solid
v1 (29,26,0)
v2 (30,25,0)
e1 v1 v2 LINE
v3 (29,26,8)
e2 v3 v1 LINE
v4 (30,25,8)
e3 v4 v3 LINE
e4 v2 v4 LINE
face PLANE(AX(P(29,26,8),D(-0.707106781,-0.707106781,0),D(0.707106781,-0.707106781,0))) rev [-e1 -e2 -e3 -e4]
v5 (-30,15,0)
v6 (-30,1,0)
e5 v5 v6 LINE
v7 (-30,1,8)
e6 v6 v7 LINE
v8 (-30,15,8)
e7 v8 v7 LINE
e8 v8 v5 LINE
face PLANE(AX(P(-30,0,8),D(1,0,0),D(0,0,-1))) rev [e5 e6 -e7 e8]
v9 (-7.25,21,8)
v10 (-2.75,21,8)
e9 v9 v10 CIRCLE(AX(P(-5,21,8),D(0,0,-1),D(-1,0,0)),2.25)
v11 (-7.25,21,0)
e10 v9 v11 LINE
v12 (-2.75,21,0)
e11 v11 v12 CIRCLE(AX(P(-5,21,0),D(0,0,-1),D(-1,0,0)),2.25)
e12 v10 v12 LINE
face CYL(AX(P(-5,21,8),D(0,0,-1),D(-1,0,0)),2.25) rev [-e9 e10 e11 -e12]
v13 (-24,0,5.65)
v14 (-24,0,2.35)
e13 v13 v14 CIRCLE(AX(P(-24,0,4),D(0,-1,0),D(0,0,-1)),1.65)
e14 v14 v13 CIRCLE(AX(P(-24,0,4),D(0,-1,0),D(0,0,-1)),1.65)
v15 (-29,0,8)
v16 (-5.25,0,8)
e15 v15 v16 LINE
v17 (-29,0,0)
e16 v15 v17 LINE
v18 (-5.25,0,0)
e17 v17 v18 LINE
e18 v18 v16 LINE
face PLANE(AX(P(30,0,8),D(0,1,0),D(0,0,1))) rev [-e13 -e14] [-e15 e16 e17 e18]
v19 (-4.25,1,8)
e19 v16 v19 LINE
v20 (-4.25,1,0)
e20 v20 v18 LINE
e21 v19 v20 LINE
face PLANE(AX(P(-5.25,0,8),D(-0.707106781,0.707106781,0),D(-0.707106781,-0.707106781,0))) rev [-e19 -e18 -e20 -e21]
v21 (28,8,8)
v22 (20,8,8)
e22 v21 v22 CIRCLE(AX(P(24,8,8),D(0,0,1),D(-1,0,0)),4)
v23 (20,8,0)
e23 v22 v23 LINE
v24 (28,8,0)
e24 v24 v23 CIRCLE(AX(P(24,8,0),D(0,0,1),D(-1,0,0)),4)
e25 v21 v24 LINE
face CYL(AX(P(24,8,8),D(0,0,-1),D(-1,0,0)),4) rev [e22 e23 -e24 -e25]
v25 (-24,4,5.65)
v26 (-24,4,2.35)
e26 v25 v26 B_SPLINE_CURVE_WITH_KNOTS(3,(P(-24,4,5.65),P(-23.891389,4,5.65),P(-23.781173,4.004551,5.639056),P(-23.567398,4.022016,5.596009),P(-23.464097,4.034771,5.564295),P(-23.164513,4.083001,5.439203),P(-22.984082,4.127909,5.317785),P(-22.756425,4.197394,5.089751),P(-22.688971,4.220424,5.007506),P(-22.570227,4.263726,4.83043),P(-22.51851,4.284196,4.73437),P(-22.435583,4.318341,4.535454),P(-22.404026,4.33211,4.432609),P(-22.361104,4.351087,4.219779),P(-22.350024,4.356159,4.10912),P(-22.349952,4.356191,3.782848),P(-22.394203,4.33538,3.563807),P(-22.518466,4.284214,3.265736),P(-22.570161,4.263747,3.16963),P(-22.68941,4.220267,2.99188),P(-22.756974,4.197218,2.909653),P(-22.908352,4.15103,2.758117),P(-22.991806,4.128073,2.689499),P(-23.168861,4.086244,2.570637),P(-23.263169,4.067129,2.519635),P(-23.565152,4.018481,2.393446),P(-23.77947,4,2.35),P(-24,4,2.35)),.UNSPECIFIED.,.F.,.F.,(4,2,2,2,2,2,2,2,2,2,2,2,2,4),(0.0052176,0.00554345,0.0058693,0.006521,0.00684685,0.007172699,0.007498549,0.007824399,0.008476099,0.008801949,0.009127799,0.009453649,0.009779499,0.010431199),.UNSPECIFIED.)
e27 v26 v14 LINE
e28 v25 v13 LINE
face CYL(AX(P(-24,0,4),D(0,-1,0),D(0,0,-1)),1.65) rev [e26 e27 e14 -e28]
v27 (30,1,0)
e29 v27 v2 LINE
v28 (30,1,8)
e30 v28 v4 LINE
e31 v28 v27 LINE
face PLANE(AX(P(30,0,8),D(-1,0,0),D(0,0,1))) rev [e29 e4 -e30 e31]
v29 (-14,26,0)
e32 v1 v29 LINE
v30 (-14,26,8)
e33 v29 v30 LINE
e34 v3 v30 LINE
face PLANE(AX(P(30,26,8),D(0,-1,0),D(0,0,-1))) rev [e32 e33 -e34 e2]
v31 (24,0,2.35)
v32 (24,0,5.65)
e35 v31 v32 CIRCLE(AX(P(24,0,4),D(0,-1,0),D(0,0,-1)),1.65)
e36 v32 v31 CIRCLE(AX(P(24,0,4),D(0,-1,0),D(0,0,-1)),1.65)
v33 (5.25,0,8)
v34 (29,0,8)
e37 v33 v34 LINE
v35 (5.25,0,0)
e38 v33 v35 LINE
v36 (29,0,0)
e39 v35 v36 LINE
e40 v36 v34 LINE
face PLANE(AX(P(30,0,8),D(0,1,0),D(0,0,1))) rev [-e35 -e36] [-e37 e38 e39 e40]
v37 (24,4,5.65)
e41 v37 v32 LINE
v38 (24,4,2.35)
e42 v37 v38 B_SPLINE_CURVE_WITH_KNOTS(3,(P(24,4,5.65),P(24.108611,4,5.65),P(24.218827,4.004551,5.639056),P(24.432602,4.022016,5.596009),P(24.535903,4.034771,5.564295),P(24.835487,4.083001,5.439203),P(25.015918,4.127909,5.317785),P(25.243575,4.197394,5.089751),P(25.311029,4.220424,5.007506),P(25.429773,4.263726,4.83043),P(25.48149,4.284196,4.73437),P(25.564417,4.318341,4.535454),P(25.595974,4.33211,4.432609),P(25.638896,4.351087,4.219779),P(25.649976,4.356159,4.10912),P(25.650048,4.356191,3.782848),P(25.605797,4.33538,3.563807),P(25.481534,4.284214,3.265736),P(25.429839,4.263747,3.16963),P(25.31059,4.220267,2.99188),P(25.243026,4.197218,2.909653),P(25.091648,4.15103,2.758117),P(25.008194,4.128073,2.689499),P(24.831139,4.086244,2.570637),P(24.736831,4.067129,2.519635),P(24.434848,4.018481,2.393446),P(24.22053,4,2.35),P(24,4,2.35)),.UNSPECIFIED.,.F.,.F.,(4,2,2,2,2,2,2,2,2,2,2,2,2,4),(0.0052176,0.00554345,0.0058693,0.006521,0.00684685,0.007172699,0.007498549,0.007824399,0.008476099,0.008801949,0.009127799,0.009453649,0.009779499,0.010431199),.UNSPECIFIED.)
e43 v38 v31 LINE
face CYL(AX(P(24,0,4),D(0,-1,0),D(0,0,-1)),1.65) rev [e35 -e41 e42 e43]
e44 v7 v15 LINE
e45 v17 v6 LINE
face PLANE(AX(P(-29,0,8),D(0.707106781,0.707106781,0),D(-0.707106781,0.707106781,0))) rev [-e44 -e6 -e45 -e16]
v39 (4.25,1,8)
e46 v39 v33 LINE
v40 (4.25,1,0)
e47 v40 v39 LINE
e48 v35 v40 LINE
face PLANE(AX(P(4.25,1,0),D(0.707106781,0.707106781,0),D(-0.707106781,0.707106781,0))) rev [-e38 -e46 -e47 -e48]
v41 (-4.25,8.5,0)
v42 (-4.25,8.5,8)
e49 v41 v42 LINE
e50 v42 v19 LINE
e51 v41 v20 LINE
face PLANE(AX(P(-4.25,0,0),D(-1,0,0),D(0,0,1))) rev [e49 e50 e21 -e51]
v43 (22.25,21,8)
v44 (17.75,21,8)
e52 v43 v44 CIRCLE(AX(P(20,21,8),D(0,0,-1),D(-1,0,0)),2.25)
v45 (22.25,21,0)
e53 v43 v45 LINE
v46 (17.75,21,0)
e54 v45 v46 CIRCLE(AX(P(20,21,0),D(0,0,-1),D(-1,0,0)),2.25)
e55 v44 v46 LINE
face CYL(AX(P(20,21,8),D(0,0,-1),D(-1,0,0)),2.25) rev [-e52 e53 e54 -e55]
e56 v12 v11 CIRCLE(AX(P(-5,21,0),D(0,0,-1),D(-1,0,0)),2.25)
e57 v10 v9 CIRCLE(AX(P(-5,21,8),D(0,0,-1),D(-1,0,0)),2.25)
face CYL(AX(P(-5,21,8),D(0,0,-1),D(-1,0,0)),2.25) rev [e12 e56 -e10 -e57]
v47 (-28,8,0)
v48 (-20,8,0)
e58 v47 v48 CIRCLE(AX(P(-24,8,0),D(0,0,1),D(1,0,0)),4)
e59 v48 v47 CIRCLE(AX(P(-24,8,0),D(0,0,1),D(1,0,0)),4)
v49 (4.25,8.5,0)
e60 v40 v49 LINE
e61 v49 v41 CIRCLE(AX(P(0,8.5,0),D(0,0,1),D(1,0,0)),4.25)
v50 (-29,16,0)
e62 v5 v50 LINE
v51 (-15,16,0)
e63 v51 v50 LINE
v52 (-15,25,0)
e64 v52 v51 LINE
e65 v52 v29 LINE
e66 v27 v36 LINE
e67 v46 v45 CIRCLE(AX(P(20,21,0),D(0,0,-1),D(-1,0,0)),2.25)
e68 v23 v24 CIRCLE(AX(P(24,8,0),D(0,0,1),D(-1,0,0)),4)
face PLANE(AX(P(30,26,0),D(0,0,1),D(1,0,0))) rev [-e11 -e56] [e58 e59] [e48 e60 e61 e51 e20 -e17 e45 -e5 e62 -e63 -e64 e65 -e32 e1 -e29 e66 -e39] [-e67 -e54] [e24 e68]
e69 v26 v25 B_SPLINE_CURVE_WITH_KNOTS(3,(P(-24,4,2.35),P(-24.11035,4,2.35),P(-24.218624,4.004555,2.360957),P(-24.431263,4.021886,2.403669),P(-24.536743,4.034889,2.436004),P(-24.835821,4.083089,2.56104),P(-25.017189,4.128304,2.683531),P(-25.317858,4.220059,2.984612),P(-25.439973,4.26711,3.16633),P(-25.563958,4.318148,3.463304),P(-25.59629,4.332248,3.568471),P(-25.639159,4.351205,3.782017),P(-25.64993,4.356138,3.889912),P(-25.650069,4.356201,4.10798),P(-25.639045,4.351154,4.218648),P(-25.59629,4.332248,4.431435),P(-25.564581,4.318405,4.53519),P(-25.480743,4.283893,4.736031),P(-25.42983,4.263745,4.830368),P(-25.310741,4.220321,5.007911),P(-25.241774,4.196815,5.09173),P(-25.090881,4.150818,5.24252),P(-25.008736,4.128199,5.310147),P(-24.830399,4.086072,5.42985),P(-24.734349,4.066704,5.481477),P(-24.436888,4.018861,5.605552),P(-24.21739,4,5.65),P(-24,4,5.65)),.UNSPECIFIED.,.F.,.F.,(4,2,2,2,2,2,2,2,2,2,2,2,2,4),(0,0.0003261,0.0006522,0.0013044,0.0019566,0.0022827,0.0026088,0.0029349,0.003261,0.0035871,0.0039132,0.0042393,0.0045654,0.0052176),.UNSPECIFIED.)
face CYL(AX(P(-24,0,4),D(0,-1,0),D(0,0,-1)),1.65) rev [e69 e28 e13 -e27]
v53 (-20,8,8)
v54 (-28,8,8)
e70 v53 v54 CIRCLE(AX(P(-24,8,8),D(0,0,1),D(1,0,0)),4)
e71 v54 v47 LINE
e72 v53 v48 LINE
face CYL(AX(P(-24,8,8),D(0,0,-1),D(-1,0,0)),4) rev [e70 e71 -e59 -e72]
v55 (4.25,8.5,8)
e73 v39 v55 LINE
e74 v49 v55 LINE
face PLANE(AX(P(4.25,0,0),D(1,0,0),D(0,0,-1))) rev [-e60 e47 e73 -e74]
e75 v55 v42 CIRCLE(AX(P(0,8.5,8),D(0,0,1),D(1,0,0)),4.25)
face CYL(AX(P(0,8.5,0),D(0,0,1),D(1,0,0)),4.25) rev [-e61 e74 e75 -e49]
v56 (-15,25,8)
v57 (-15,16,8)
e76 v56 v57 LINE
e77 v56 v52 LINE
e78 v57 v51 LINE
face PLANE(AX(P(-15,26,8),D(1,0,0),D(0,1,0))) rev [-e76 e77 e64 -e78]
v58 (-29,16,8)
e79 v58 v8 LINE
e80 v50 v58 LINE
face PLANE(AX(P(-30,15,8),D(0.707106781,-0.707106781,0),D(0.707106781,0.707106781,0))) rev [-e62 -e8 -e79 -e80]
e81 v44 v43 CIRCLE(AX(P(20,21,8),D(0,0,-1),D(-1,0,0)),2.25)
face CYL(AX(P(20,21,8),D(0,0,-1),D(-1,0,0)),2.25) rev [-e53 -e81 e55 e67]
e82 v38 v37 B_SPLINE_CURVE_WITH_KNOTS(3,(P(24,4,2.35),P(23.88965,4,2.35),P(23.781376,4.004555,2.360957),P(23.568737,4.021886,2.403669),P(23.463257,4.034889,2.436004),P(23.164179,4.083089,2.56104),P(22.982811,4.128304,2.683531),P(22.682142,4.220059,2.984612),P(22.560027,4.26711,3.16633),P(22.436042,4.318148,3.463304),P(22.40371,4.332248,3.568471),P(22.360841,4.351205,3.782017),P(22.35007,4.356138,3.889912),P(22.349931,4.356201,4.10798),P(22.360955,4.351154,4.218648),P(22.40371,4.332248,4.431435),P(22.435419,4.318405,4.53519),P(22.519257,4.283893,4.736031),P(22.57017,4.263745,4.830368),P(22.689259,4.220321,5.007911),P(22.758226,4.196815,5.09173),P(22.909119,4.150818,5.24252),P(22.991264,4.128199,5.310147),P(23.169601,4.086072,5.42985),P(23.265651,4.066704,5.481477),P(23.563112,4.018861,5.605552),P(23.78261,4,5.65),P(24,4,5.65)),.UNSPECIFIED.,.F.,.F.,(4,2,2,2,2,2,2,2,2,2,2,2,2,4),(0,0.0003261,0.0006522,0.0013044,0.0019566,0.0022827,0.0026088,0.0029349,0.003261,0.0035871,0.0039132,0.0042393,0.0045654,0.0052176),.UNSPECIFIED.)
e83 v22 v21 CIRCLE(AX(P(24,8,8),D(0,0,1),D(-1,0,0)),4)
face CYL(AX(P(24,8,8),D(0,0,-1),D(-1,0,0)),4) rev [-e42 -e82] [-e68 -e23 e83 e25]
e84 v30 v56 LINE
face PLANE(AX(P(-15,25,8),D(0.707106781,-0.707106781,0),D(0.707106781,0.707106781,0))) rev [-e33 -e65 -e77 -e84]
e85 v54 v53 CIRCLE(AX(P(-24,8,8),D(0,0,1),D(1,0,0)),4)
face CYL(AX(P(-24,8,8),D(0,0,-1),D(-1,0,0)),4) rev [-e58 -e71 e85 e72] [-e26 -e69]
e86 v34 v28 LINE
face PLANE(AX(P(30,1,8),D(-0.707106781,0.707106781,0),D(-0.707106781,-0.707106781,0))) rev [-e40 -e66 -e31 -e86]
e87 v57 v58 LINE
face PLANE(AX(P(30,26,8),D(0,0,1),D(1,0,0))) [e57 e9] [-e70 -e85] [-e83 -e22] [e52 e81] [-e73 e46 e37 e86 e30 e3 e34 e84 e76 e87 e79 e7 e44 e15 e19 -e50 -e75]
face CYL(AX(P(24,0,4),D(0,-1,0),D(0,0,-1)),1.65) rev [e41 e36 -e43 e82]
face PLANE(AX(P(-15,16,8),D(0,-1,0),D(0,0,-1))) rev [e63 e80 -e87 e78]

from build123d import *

# Parameters (mm, degrees)
SKETCH1_W              = 60
SKETCH1_H              = 26
SKETCH1_R              = 4
BOSS_EXTRUDE1_DEPTH    = 8
CUT_EXTRUDE1_DEPTH     = 41.496913463
M4_TAPPED_HOLE1_REACH  = 42.497
M4_TAPPED_HOLE1_BORE_R = 1.65
SKETCH8_W              = 15
SKETCH8_H              = 10
CUT_EXTRUDE2_DEPTH     = 41.496913482
SKETCH9_R              = 2.25
CUT_EXTRUDE3_DEPTH     = 41.496913482
CHAMFER1_SIZE          = 1


with BuildPart() as part:
    # Sketch1 → Boss-Extrude1 (new body)
    with BuildSketch(Plane.XY):
        with Locations((0, 13)):
            Rectangle(SKETCH1_W, SKETCH1_H)
        with Locations((-24, 8)):
            Circle(SKETCH1_R, mode=Mode.SUBTRACT)
        with Locations(Location((24, 8, 0), (0, 0, 180))):
            Circle(SKETCH1_R, mode=Mode.SUBTRACT)
    extrude(amount=BOSS_EXTRUDE1_DEPTH)

    # Sketch2 → Cut-Extrude1 (cut, through all)
    with BuildSketch(Plane.XY.offset(8)):
        with BuildLine():
            Line((-4.25, 0), (-4.25, 8.5))
            ThreePointArc((-4.25, 8.5), (0, 12.75), (4.25, 8.5))
            Line((4.25, 8.5), (4.25, 0))
            ThreePointArc((4.25, 0), (0, -4.25), (-4.25, 0))
        make_face()
    extrude(amount=-CUT_EXTRUDE1_DEPTH, mode=Mode.SUBTRACT)

    # M4 Tapped Hole1 bore → M4 Tapped Hole1 (cut, up to next)
    with BuildSketch(Plane.XZ, mode=Mode.PRIVATE) as m4_tapped_hole1_sk1:
        with Locations((-24, 4)):
            Circle(M4_TAPPED_HOLE1_BORE_R)
    m4_tapped_hole1_tool1 = extrude(m4_tapped_hole1_sk1.sketch, amount=-M4_TAPPED_HOLE1_REACH, mode=Mode.PRIVATE) & part.part
    # M4 Tapped Hole1 bore → M4 Tapped Hole1 (cut, up to next)
    with BuildSketch(Plane.XZ, mode=Mode.PRIVATE) as m4_tapped_hole1_sk2:
        with Locations((24, 4)):
            Circle(M4_TAPPED_HOLE1_BORE_R)
    m4_tapped_hole1_tool2 = extrude(m4_tapped_hole1_sk2.sketch, amount=-M4_TAPPED_HOLE1_REACH, mode=Mode.PRIVATE) & part.part
    add(m4_tapped_hole1_tool1.solids().sort_by_distance((-24, 0, 4))[0], mode=Mode.SUBTRACT)
    add(m4_tapped_hole1_tool2.solids().sort_by_distance((24, 0, 4))[0], mode=Mode.SUBTRACT)

    # Sketch8 → Cut-Extrude2 (cut, through all)
    with BuildSketch(Plane(origin=(0, 0, 0), x_dir=(-1, 0, 0), z_dir=(0, 0, -1))):
        with Locations((22.5, 21)):
            Rectangle(SKETCH8_W, SKETCH8_H)
    extrude(amount=-CUT_EXTRUDE2_DEPTH, mode=Mode.SUBTRACT)

    # Sketch9 → Cut-Extrude3 (cut, through all)
    with BuildSketch(Plane(origin=(0, 0, 0), x_dir=(-1, 0, 0), z_dir=(0, 0, -1))):
        with Locations((-20, 21)):
            Circle(SKETCH9_R)
        with Locations((5, 21)):
            Circle(SKETCH9_R)
    extrude(amount=-CUT_EXTRUDE3_DEPTH, mode=Mode.SUBTRACT)

    # Chamfer1
    chamfer1_edges = [part.edges().sort_by_distance(p)[0] for p in [
        (4.25, 0, 4),
        (-4.25, 0, 4),
        (-15, 26, 4),
        (-30, 16, 4),
        (30, 0, 4),
        (-30, 0, 4),
        (30, 26, 4),
    ]]
    chamfer(chamfer1_edges, length=CHAMFER1_SIZE)


solid = part.part
